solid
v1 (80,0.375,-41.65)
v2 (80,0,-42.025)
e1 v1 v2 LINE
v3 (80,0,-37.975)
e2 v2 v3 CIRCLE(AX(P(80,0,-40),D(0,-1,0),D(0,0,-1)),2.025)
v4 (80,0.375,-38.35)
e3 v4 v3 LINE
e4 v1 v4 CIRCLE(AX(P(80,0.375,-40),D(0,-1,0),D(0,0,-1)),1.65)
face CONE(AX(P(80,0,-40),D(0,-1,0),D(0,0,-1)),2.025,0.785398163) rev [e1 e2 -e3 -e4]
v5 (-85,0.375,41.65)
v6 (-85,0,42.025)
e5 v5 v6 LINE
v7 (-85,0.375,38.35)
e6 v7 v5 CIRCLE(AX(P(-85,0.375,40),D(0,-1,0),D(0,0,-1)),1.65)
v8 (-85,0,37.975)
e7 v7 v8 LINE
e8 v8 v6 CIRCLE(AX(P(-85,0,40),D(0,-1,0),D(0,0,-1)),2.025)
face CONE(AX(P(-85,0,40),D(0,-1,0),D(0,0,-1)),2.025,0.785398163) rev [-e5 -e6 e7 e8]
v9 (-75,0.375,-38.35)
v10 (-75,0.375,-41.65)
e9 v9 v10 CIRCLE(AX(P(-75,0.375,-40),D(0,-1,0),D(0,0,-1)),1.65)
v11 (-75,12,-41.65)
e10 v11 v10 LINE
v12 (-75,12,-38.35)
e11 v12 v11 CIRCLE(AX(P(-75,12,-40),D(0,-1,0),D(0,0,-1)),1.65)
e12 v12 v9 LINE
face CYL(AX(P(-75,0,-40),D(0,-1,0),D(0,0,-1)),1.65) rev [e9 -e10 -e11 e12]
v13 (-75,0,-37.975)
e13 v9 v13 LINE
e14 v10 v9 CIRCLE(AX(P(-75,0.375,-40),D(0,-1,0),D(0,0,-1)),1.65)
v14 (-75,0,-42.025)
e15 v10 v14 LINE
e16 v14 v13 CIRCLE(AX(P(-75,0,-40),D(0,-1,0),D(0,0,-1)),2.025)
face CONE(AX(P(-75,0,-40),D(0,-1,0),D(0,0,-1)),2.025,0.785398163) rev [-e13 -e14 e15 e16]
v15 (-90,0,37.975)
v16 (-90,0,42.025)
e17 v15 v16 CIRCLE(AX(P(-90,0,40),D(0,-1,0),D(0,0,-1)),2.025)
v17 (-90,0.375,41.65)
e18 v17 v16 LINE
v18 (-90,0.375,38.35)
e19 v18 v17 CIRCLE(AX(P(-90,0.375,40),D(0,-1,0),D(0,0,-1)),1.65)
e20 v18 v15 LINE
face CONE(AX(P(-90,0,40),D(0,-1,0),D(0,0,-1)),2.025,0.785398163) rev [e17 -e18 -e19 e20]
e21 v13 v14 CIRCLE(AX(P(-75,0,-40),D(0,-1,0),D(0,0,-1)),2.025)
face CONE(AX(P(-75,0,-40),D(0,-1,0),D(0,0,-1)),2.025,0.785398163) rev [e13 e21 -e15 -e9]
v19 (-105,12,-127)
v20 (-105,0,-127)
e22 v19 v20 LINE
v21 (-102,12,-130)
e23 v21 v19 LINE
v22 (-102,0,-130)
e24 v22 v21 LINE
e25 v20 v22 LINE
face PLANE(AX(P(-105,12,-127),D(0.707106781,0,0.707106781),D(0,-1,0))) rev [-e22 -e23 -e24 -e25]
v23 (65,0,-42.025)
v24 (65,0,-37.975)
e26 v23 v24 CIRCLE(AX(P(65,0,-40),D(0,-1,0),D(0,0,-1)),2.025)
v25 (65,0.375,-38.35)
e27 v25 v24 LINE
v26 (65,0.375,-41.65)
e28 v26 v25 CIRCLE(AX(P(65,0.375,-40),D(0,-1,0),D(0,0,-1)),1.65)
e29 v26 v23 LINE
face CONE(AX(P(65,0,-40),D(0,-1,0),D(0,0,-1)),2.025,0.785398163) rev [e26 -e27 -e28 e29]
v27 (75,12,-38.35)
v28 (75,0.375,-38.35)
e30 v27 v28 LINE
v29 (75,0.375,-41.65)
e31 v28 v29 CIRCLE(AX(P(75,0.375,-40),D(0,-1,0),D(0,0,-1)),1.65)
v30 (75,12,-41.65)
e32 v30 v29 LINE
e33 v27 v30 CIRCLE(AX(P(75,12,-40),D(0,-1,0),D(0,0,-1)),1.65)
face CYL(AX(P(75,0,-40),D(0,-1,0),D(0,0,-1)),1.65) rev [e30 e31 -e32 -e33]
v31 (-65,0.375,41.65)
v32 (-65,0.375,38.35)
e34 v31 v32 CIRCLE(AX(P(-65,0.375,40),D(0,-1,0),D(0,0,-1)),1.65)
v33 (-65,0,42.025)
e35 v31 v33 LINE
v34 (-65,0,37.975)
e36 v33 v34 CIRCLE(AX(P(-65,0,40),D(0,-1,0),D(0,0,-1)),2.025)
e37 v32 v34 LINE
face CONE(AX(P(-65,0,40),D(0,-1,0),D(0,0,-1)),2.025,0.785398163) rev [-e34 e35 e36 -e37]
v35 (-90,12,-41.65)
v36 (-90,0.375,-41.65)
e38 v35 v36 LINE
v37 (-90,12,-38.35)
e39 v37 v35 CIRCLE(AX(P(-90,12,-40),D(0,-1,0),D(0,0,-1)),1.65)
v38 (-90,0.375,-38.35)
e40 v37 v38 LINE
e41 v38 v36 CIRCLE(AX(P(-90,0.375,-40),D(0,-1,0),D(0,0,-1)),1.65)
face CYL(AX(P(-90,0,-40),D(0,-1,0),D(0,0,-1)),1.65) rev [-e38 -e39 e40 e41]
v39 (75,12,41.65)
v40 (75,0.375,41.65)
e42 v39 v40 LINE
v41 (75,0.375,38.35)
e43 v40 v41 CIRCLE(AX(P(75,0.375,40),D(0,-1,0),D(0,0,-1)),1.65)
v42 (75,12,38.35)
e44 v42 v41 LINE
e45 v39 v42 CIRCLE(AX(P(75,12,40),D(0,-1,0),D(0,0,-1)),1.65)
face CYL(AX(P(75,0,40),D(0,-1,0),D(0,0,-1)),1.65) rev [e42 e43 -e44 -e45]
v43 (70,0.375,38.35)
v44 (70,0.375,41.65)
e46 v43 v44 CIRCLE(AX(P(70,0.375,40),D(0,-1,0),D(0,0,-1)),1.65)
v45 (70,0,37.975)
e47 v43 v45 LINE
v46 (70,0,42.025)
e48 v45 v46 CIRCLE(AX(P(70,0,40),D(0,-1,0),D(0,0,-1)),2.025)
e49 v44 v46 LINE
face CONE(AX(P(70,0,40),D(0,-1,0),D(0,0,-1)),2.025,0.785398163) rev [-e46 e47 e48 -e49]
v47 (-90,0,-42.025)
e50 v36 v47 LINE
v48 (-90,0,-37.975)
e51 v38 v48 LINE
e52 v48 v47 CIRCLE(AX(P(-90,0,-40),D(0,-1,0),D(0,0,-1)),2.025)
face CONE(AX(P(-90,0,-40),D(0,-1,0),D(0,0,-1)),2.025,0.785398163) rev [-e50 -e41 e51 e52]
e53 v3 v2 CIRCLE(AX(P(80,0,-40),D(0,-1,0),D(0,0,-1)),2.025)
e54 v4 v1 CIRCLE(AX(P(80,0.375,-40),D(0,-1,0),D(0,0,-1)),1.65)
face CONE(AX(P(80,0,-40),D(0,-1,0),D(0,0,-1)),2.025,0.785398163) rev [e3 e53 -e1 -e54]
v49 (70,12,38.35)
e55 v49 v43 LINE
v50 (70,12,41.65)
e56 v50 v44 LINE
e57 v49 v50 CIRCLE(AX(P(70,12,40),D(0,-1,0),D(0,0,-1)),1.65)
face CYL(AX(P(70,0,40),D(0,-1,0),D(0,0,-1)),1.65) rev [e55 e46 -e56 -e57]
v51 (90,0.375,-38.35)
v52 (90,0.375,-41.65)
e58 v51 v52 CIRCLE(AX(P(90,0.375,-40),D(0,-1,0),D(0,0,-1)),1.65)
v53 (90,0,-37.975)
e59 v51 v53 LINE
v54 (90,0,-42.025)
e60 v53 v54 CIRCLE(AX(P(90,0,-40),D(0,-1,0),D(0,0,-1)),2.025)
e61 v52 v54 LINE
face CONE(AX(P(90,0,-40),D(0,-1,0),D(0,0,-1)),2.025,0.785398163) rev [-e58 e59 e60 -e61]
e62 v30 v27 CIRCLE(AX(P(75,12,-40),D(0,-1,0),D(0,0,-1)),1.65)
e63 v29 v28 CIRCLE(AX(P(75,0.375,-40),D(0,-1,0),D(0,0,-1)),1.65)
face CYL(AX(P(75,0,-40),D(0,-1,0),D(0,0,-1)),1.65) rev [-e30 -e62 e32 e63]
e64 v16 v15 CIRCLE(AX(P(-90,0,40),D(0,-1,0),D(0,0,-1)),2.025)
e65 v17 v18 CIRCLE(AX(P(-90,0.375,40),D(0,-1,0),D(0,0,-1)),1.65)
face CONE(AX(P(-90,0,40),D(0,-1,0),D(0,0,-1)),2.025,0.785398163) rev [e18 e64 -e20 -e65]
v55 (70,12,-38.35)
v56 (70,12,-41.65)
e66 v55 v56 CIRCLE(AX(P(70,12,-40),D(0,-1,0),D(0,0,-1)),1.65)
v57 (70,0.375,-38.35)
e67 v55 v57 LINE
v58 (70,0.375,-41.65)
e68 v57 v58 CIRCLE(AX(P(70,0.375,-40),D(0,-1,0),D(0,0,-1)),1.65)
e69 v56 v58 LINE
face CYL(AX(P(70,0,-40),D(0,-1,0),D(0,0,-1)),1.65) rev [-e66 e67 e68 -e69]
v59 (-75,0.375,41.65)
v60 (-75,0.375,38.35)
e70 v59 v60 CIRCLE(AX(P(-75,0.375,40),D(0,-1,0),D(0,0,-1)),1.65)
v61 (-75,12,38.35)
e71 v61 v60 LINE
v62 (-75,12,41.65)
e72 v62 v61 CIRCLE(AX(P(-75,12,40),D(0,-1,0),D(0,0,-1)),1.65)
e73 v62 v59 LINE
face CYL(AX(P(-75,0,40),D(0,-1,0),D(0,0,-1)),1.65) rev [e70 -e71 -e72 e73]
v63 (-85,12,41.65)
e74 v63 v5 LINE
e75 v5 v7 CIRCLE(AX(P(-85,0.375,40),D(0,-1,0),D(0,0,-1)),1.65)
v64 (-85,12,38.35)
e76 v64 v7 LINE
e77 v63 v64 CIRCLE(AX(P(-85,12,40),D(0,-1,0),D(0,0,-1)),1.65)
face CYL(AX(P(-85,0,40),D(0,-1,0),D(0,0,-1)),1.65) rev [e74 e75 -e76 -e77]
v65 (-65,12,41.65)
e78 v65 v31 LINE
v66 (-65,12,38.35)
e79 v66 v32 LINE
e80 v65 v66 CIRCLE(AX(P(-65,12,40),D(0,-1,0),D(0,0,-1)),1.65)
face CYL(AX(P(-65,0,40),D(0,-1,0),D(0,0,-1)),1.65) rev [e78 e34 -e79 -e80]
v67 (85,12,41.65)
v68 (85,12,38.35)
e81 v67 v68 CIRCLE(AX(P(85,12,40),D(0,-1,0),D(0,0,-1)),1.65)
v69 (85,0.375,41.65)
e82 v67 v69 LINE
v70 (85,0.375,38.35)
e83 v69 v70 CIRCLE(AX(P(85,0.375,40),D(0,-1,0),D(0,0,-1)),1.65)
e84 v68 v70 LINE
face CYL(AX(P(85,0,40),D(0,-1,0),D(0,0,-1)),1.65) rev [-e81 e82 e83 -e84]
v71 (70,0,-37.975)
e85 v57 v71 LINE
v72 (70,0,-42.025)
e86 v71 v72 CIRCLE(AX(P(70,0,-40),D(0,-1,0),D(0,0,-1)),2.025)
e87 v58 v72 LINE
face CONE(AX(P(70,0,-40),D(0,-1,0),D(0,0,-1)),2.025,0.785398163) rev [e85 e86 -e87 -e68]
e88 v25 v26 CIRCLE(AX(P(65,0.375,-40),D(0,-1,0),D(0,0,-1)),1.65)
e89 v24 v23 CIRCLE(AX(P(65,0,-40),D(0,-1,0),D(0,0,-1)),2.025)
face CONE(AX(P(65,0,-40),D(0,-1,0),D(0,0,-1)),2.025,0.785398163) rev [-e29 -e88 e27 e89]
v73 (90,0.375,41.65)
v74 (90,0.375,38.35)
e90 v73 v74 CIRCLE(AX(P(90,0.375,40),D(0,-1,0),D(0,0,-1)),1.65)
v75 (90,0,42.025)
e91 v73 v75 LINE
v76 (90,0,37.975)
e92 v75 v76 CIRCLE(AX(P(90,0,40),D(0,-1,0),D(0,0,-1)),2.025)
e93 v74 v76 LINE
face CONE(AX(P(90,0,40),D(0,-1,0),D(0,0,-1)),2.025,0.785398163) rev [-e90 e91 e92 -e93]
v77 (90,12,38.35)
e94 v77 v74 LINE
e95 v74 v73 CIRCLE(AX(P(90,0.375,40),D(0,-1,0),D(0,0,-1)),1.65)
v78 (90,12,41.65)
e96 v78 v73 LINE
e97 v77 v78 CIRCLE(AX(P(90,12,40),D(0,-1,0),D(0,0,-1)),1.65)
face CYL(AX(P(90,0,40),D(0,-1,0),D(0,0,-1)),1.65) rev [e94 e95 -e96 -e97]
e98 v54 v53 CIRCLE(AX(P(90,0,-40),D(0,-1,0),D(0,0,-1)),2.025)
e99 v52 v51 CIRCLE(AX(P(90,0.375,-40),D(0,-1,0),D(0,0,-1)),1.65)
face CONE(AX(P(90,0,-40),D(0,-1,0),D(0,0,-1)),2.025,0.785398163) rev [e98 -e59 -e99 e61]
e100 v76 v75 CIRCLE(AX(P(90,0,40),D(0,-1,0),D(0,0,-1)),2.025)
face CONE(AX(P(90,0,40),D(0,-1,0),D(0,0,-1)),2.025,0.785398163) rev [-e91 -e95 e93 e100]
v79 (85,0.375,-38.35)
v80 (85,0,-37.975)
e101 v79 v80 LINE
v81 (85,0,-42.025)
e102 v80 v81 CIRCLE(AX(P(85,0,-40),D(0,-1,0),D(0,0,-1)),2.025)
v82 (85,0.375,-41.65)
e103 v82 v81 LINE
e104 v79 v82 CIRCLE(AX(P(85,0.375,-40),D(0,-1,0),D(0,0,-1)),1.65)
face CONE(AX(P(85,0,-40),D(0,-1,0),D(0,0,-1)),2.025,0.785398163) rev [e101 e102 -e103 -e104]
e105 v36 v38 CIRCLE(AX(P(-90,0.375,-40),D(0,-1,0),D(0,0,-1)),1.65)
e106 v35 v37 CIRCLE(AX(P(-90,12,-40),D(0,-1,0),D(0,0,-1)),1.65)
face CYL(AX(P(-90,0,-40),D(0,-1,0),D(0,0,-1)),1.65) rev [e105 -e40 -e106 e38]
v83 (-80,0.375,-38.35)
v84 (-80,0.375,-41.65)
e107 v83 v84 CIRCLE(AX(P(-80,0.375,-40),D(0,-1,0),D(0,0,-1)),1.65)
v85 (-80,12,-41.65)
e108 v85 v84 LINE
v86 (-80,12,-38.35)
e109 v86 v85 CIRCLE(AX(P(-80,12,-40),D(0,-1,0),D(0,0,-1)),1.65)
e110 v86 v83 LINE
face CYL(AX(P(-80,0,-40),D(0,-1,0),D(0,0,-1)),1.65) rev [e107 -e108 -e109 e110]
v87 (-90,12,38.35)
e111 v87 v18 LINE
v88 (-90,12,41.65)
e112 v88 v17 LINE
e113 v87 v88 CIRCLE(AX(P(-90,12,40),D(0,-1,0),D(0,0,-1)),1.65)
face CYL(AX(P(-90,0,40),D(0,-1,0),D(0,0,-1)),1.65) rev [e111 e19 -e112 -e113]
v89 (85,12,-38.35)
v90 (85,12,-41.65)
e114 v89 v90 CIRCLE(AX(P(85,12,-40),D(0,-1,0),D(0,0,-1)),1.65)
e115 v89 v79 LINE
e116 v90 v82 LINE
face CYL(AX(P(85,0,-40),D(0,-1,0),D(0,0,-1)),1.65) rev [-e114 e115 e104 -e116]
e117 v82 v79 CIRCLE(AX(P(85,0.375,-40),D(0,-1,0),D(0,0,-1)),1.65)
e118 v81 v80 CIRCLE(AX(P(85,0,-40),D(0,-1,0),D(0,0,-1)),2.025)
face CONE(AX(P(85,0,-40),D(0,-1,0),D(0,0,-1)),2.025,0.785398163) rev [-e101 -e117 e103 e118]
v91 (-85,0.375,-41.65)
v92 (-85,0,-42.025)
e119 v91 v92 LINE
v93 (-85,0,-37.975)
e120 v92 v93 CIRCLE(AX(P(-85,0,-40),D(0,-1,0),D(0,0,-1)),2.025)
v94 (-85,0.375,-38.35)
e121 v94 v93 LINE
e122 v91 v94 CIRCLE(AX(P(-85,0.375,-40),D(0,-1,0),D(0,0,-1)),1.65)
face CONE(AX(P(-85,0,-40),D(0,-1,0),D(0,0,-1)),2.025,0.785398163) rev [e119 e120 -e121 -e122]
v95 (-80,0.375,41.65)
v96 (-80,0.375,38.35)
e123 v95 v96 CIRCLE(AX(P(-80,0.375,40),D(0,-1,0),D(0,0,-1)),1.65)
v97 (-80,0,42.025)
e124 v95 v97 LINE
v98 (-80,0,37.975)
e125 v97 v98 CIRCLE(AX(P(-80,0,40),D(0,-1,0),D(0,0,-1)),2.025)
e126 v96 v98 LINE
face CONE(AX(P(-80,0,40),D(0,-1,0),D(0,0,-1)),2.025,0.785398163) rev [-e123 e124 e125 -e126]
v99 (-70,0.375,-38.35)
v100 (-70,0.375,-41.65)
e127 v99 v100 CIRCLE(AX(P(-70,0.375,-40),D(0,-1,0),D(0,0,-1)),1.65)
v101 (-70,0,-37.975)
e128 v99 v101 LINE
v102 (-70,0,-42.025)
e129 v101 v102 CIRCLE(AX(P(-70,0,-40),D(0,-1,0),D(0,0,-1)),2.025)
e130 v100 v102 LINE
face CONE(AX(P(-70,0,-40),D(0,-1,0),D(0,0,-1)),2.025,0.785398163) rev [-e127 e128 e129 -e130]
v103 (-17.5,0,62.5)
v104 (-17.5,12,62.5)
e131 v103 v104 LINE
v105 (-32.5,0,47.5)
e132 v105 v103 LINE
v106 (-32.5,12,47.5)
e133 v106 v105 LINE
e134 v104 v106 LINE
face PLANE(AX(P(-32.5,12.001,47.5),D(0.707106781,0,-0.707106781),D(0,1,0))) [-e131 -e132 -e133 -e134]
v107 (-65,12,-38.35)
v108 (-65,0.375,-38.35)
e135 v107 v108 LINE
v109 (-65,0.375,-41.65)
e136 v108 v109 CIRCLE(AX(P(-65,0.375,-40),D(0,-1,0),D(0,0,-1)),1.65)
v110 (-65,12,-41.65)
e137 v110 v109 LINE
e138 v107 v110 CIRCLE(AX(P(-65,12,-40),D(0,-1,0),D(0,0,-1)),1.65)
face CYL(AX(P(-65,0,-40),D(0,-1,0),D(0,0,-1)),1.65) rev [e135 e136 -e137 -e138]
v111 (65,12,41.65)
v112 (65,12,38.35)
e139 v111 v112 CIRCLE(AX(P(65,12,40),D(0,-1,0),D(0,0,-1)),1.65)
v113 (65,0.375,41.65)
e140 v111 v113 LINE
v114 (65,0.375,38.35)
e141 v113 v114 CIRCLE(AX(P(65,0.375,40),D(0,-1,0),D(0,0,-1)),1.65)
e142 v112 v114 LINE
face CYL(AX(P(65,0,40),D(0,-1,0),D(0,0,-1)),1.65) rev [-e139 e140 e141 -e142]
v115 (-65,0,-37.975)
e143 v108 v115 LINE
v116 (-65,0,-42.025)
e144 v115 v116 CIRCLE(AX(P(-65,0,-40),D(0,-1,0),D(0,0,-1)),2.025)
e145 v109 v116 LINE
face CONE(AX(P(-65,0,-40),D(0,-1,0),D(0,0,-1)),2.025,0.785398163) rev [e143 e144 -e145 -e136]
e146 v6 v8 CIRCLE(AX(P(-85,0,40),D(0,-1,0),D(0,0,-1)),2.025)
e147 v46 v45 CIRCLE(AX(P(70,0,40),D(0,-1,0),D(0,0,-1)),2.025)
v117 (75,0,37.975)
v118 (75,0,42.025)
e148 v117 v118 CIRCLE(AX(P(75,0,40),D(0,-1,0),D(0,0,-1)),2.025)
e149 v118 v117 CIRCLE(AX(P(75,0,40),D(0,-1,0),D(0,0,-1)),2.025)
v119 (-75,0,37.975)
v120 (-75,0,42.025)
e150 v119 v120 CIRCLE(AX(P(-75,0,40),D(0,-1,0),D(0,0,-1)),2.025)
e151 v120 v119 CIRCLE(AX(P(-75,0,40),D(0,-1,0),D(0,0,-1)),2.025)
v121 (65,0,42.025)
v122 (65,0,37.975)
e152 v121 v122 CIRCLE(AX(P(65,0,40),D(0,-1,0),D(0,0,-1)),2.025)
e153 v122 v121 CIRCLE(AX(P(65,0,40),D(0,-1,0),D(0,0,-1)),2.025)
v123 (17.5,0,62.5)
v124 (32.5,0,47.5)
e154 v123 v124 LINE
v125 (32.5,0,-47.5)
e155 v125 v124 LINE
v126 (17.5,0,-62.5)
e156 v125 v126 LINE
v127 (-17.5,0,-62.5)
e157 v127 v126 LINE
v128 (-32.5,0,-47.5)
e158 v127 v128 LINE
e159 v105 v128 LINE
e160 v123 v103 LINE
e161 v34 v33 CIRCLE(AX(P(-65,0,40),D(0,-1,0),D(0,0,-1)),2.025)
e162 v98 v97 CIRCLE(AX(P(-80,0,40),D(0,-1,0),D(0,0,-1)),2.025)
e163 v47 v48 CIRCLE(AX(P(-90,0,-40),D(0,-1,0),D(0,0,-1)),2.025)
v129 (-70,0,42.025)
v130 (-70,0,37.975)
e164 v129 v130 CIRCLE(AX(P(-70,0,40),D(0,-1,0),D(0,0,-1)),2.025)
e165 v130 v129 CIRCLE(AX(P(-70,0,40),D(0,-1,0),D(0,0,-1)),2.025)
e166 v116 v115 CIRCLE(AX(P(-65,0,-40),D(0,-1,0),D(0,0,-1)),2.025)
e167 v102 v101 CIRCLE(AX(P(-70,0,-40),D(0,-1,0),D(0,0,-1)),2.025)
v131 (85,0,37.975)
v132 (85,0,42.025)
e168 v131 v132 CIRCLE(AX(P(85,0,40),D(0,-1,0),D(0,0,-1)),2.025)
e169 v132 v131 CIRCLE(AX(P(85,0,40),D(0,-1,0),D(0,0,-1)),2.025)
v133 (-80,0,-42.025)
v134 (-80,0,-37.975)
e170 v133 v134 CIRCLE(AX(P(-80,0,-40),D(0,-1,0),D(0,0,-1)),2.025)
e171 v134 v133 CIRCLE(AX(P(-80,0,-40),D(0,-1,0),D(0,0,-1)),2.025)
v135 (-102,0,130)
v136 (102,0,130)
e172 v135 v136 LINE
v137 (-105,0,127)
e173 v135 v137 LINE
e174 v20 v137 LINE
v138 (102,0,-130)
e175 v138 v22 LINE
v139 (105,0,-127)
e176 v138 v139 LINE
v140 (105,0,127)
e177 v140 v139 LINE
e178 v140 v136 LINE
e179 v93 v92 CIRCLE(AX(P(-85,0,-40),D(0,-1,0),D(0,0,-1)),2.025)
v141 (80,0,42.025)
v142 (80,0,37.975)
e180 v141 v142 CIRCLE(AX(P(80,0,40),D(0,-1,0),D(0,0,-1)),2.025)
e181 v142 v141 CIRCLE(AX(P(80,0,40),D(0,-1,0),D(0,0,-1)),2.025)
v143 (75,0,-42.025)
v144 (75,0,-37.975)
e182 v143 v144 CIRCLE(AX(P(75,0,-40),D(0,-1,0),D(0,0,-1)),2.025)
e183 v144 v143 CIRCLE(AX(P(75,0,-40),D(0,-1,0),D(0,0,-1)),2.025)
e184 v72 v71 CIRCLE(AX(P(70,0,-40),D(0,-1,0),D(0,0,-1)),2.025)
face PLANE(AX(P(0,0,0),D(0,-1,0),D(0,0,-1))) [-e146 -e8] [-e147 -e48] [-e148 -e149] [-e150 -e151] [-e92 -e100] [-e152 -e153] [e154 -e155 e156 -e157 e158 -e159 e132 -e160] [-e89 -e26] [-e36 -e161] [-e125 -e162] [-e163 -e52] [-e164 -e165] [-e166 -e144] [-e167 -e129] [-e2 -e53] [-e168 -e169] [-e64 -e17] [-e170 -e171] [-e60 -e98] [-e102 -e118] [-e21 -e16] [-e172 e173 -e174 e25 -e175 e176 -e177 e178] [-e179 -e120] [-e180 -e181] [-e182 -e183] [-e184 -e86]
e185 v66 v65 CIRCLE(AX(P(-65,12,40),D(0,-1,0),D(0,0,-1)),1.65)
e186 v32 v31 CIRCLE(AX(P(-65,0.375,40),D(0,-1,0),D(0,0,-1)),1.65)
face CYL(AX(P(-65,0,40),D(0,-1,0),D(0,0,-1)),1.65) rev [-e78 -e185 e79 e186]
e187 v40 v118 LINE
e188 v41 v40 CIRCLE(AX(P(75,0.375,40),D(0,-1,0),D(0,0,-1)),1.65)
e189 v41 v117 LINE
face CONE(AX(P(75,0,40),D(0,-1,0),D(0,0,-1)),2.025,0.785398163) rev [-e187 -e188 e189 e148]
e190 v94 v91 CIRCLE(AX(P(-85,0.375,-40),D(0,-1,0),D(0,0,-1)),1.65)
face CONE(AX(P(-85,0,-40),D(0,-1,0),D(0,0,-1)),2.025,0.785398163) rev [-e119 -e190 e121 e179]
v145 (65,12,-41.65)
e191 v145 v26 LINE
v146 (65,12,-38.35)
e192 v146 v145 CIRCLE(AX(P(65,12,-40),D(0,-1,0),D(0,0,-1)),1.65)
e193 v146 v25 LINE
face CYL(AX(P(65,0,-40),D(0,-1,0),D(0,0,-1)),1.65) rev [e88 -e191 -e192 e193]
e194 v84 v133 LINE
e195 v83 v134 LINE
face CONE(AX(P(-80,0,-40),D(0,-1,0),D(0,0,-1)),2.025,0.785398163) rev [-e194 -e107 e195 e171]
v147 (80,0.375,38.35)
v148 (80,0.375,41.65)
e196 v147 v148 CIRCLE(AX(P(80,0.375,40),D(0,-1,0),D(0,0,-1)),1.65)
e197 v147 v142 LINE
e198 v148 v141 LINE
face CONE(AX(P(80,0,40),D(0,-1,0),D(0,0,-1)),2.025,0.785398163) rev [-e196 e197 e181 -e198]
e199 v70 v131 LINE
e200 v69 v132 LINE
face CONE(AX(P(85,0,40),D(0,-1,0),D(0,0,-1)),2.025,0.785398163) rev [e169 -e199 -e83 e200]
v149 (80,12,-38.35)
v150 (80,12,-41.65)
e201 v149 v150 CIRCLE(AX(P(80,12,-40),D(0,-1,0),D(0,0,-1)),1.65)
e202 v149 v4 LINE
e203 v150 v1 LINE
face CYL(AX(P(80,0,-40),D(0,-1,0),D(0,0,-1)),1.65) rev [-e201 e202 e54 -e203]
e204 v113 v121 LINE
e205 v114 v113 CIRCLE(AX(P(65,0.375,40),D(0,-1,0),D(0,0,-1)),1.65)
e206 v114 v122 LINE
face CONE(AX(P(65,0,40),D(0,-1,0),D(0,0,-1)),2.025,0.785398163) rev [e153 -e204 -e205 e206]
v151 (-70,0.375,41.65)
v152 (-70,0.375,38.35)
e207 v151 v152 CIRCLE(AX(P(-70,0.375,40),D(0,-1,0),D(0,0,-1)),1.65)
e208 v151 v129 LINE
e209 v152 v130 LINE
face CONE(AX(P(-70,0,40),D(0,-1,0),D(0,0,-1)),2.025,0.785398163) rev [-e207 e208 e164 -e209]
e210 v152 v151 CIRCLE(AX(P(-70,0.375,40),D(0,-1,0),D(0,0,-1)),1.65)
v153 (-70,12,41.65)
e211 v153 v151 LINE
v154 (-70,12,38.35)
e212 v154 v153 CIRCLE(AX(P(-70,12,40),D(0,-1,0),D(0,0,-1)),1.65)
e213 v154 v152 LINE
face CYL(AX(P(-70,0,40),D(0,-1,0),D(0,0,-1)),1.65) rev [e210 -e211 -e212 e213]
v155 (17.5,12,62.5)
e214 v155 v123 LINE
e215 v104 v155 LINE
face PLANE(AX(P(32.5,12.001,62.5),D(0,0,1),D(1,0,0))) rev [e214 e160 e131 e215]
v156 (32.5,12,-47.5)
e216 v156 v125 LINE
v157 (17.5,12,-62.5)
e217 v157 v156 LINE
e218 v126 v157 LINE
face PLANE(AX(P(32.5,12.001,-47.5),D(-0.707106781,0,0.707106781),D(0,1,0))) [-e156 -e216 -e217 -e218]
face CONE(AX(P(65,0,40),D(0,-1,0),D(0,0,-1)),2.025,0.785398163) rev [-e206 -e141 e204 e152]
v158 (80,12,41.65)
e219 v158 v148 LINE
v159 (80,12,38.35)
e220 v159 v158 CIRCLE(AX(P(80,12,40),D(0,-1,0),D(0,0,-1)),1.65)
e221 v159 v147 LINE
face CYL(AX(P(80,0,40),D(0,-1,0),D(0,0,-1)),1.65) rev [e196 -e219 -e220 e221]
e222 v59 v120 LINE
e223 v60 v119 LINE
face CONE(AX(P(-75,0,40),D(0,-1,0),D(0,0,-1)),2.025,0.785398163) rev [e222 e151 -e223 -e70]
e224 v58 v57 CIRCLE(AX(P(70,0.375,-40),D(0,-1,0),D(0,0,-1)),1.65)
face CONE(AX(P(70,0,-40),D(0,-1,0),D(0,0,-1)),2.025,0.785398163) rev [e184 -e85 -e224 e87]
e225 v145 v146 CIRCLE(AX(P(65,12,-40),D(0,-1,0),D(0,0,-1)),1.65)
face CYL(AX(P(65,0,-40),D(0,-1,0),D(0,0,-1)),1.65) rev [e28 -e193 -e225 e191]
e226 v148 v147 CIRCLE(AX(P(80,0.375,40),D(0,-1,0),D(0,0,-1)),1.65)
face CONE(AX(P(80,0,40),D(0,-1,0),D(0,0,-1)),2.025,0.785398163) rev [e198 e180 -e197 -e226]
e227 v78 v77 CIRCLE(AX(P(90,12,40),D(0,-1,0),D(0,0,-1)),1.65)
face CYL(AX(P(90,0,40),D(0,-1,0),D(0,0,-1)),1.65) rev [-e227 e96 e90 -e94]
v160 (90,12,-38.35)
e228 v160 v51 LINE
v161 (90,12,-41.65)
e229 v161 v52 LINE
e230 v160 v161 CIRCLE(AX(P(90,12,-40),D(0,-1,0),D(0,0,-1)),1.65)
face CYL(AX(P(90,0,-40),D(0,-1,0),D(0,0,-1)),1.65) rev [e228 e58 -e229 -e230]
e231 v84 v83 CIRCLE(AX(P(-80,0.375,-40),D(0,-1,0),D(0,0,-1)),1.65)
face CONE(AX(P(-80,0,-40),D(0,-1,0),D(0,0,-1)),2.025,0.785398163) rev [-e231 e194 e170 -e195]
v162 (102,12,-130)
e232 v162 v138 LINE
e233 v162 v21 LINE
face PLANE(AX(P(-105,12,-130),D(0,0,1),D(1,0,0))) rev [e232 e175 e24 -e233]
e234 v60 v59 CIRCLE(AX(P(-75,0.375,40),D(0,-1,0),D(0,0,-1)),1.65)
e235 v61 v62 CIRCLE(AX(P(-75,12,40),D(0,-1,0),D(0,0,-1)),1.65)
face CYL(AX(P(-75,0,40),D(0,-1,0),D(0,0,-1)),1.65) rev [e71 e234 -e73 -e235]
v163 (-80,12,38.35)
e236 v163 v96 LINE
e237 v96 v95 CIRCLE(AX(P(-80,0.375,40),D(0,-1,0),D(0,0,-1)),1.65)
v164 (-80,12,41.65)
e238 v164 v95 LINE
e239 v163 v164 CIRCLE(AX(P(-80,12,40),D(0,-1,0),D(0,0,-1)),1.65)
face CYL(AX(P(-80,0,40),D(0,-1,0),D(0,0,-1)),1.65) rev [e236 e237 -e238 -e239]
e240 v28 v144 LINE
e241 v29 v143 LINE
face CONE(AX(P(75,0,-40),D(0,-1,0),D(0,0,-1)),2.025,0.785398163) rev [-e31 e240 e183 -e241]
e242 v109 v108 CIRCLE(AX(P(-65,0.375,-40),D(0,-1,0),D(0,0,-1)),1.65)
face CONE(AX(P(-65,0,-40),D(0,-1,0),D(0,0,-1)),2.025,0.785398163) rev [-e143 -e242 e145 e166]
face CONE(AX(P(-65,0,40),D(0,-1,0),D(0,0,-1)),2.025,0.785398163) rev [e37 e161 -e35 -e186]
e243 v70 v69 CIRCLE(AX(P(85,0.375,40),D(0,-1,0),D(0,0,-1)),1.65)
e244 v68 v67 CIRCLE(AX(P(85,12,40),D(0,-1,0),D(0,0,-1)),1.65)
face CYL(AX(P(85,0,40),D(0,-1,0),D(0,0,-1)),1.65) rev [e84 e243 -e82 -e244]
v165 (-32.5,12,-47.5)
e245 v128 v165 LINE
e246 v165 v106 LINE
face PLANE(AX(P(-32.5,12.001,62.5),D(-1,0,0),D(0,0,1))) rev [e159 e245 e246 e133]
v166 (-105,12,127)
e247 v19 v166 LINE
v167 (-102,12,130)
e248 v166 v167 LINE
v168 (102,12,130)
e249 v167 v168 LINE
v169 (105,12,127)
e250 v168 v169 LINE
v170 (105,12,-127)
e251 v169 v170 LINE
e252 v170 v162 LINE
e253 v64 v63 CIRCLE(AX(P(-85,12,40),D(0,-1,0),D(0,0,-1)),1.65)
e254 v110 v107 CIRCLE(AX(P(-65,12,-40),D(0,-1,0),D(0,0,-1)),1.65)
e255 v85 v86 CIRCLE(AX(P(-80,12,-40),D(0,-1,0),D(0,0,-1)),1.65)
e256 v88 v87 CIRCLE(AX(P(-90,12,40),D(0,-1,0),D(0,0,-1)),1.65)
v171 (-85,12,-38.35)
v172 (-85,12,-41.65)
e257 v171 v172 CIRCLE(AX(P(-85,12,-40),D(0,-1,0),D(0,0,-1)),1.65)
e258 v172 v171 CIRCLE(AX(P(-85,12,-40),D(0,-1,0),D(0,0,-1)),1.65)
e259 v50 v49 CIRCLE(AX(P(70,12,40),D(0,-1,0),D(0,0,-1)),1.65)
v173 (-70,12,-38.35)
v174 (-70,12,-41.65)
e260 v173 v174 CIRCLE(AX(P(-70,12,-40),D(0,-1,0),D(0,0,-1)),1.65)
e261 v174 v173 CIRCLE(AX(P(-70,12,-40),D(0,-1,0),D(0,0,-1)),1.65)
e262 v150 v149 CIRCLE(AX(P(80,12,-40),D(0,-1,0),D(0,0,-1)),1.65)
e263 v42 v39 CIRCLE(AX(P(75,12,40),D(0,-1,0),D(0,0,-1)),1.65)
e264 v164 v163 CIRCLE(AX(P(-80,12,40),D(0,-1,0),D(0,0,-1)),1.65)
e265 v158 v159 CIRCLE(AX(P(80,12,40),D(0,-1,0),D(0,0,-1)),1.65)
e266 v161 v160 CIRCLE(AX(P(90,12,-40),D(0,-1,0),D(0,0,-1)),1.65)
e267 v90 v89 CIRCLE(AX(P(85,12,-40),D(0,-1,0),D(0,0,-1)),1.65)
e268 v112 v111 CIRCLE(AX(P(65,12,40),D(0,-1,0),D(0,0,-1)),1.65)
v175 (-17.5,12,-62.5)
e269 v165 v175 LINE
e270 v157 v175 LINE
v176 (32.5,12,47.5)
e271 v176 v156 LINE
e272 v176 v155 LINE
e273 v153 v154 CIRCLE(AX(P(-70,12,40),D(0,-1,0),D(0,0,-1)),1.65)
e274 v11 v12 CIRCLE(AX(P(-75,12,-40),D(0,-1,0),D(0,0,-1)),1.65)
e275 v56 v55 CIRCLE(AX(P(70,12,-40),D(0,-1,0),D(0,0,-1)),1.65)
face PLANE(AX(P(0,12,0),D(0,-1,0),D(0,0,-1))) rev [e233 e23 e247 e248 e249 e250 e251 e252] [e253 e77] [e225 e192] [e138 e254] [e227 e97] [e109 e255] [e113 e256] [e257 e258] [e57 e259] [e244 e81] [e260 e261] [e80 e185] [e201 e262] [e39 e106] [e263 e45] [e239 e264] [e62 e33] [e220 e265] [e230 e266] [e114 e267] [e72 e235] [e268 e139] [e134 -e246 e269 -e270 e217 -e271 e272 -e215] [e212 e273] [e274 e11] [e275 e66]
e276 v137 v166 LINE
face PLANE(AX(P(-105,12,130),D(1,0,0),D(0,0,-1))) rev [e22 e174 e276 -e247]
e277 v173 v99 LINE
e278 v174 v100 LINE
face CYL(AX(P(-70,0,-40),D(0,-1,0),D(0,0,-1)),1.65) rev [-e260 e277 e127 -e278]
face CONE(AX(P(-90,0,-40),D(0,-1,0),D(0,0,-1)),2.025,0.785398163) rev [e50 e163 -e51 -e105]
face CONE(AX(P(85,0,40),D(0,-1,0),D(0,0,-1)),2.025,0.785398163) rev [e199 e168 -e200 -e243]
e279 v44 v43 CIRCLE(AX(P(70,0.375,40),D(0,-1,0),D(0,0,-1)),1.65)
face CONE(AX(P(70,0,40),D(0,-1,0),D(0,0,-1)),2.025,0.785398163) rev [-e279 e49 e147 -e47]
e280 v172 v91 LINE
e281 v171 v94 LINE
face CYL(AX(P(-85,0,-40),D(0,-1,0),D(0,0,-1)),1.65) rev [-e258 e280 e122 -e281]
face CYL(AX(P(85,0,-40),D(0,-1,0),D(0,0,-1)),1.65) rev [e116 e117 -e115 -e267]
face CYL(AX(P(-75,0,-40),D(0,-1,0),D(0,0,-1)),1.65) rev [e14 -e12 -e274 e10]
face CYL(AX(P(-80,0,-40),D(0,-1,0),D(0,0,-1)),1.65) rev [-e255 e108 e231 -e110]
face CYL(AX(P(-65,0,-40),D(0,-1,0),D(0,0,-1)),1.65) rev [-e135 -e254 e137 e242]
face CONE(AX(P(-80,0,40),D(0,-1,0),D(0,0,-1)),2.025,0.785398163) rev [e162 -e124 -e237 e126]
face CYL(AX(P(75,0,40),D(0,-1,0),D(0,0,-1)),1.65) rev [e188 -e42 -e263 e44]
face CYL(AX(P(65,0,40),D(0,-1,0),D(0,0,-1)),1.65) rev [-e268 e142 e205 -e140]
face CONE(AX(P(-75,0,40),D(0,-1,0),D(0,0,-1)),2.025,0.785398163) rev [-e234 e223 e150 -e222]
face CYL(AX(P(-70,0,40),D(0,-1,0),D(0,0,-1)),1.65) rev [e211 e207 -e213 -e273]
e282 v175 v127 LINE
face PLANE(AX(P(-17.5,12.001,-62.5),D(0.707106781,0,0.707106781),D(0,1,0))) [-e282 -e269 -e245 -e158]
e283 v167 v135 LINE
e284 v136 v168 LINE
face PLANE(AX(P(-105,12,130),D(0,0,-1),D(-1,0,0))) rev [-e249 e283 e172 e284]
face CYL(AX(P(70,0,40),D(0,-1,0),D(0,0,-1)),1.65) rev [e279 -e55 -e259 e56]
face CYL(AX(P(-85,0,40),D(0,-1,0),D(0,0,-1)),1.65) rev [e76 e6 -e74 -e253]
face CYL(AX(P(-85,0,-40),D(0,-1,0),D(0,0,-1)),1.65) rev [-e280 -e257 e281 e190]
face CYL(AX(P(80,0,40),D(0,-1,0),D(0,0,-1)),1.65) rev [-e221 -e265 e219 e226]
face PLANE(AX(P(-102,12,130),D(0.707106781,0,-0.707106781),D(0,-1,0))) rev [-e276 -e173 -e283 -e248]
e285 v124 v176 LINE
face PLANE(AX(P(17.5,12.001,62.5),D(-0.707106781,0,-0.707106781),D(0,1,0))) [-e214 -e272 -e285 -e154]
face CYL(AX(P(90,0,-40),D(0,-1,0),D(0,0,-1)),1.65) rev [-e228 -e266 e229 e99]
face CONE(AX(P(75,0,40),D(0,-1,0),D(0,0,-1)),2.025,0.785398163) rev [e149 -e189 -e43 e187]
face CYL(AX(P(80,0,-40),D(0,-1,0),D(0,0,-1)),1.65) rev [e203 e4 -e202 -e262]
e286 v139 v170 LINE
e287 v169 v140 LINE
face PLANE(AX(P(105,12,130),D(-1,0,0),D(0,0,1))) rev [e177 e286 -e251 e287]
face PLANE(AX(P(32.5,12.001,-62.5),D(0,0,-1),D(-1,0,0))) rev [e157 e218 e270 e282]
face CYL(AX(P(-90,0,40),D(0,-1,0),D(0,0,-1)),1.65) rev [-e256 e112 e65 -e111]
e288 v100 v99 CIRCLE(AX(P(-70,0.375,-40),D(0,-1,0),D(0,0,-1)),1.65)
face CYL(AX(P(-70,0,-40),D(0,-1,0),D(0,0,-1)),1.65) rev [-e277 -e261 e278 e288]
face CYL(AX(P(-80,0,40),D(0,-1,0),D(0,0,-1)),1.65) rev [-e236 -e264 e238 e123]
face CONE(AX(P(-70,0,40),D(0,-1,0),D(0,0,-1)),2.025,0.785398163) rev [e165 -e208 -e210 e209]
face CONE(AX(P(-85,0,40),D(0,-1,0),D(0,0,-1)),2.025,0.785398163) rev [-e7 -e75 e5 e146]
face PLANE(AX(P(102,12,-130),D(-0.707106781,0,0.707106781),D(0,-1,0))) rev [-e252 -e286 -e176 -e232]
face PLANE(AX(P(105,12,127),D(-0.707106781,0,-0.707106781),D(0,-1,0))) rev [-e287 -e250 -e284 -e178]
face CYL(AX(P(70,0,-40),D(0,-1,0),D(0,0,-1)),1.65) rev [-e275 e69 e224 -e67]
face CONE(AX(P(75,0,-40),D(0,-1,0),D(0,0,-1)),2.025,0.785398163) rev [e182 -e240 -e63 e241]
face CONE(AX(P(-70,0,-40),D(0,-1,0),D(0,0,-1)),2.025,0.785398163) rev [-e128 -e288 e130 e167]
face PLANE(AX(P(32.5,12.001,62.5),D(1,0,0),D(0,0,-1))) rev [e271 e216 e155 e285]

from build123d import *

# Parameters (mm, degrees)
SKETCH_1_W                   = 210
SKETCH_1_H                   = 260
EXTRUDE_1_DEPTH              = 12
HOLE_WIZARD_M4_1_D           = 3.3
HOLE_WIZARD_M4_1_CSINK_D     = 4.05
HOLE_WIZARD_M4_1_CSINK_ANGLE = 90
PATTERN_LINEAR_1_COUNT       = 6
PATTERN_LINEAR_1_PITCH       = 5
MIRROR_1_COPY_1_D            = 3.3
MIRROR_1_COPY_1_CSINK_D      = 4.05
MIRROR_1_COPY_1_CSINK_ANGLE  = 90
MIRROR_1_COPY_2_D            = 3.3
MIRROR_1_COPY_2_CSINK_D      = 4.05
MIRROR_1_COPY_2_CSINK_ANGLE  = 90
MIRROR_1_COPY_3_D            = 3.3
MIRROR_1_COPY_3_CSINK_D      = 4.05
MIRROR_1_COPY_3_CSINK_ANGLE  = 90
MIRROR_1_COPY_4_D            = 3.3
MIRROR_1_COPY_4_CSINK_D      = 4.05
MIRROR_1_COPY_4_CSINK_ANGLE  = 90
MIRROR_1_COPY_5_D            = 3.3
MIRROR_1_COPY_5_CSINK_D      = 4.05
MIRROR_1_COPY_5_CSINK_ANGLE  = 90
MIRROR_2_COPY_1_D            = 3.3
MIRROR_2_COPY_1_CSINK_D      = 4.05
MIRROR_2_COPY_1_CSINK_ANGLE  = 90
MIRROR_2_COPY_2_D            = 3.3
MIRROR_2_COPY_2_CSINK_D      = 4.05
MIRROR_2_COPY_2_CSINK_ANGLE  = 90
MIRROR_2_COPY_3_D            = 3.3
MIRROR_2_COPY_3_CSINK_D      = 4.05
MIRROR_2_COPY_3_CSINK_ANGLE  = 90
MIRROR_2_COPY_4_D            = 3.3
MIRROR_2_COPY_4_CSINK_D      = 4.05
MIRROR_2_COPY_4_CSINK_ANGLE  = 90
MIRROR_2_COPY_5_D            = 3.3
MIRROR_2_COPY_5_CSINK_D      = 4.05
MIRROR_2_COPY_5_CSINK_ANGLE  = 90
MIRROR_2_COPY_6_D            = 3.3
MIRROR_2_COPY_6_CSINK_D      = 4.05
MIRROR_2_COPY_6_CSINK_ANGLE  = 90
MIRROR_2_COPY_7_D            = 3.3
MIRROR_2_COPY_7_CSINK_D      = 4.05
MIRROR_2_COPY_7_CSINK_ANGLE  = 90
MIRROR_2_COPY_8_D            = 3.3
MIRROR_2_COPY_8_CSINK_D      = 4.05
MIRROR_2_COPY_8_CSINK_ANGLE  = 90
MIRROR_2_COPY_9_D            = 3.3
MIRROR_2_COPY_9_CSINK_D      = 4.05
MIRROR_2_COPY_9_CSINK_ANGLE  = 90
MIRROR_2_COPY_10_D           = 3.3
MIRROR_2_COPY_10_CSINK_D     = 4.05
MIRROR_2_COPY_10_CSINK_ANGLE = 90
MIRROR_2_COPY_11_D           = 3.3
MIRROR_2_COPY_11_CSINK_D     = 4.05
MIRROR_2_COPY_11_CSINK_ANGLE = 90
CHAMFER_1_SIZE               = 3
CUT_EXTRUDE_1_REACH          = 169.538
SKETCH_3_W                   = 65
SKETCH_3_H                   = 125
CHAMFER_2_SIZE               = 15


with BuildPart() as part:
    # 草图1 → 凸台-拉伸1 (new body)
    with BuildSketch(Plane(origin=(0, 0, 0), x_dir=(1, 0, 0), z_dir=(0, 1, 0))):
        Rectangle(SKETCH_1_W, SKETCH_1_H)
    extrude(amount=EXTRUDE_1_DEPTH)

    # M4 螺纹孔1 (through all)
    with Locations(Plane(origin=(-90, 0, -40), x_dir=(0, 0, -1), z_dir=(0, -1, 0))):
        with Locations((0, 0)):
            hole_wizard_m4_1 = CounterSinkHole(HOLE_WIZARD_M4_1_D / 2, HOLE_WIZARD_M4_1_CSINK_D / 2, counter_sink_angle=HOLE_WIZARD_M4_1_CSINK_ANGLE)

    # 阵列(线性)1: M4 螺纹孔1 ×6
    with Locations(*[(i * PATTERN_LINEAR_1_PITCH, 0, 0) for i in range(1, PATTERN_LINEAR_1_COUNT)]):
        add(hole_wizard_m4_1, mode=Mode.SUBTRACT)

    # 镜向1: M4 螺纹孔1 across plane
    add(hole_wizard_m4_1.mirror(Plane(origin=(0, 0, 0), x_dir=(0, 0, 1), z_dir=(1, 0, 0))), mode=Mode.SUBTRACT)

    # 镜向1 copy 1 (through all)
    with Locations(Plane(origin=(85, 0, -40), x_dir=(0, 0, -1), z_dir=(0, -1, 0))):
        with Locations((0, 0)):
            CounterSinkHole(MIRROR_1_COPY_1_D / 2, MIRROR_1_COPY_1_CSINK_D / 2, counter_sink_angle=MIRROR_1_COPY_1_CSINK_ANGLE)

    # 镜向1 copy 2 (through all)
    with Locations(Plane(origin=(80, 0, -40), x_dir=(0, 0, -1), z_dir=(0, -1, 0))):
        with Locations((0, 0)):
            CounterSinkHole(MIRROR_1_COPY_2_D / 2, MIRROR_1_COPY_2_CSINK_D / 2, counter_sink_angle=MIRROR_1_COPY_2_CSINK_ANGLE)

    # 镜向1 copy 3 (through all)
    with Locations(Plane(origin=(75, 0, -40), x_dir=(0, 0, -1), z_dir=(0, -1, 0))):
        with Locations((0, 0)):
            CounterSinkHole(MIRROR_1_COPY_3_D / 2, MIRROR_1_COPY_3_CSINK_D / 2, counter_sink_angle=MIRROR_1_COPY_3_CSINK_ANGLE)

    # 镜向1 copy 4 (through all)
    with Locations(Plane(origin=(70, 0, -40), x_dir=(0, 0, -1), z_dir=(0, -1, 0))):
        with Locations((0, 0)):
            CounterSinkHole(MIRROR_1_COPY_4_D / 2, MIRROR_1_COPY_4_CSINK_D / 2, counter_sink_angle=MIRROR_1_COPY_4_CSINK_ANGLE)

    # 镜向1 copy 5 (through all)
    with Locations(Plane(origin=(65, 0, -40), x_dir=(0, 0, -1), z_dir=(0, -1, 0))):
        with Locations((0, 0)):
            CounterSinkHole(MIRROR_1_COPY_5_D / 2, MIRROR_1_COPY_5_CSINK_D / 2, counter_sink_angle=MIRROR_1_COPY_5_CSINK_ANGLE)

    # 镜向2: M4 螺纹孔1 across plane
    add(hole_wizard_m4_1.mirror(Plane.XY), mode=Mode.SUBTRACT)

    # 镜向2 copy 1 (through all)
    with Locations(Plane(origin=(-85, 0, 40), x_dir=(0, 0, 1), z_dir=(0, -1, 0))):
        with Locations((0, 0)):
            CounterSinkHole(MIRROR_2_COPY_1_D / 2, MIRROR_2_COPY_1_CSINK_D / 2, counter_sink_angle=MIRROR_2_COPY_1_CSINK_ANGLE)

    # 镜向2 copy 2 (through all)
    with Locations(Plane(origin=(-80, 0, 40), x_dir=(0, 0, 1), z_dir=(0, -1, 0))):
        with Locations((0, 0)):
            CounterSinkHole(MIRROR_2_COPY_2_D / 2, MIRROR_2_COPY_2_CSINK_D / 2, counter_sink_angle=MIRROR_2_COPY_2_CSINK_ANGLE)

    # 镜向2 copy 3 (through all)
    with Locations(Plane(origin=(-75, 0, 40), x_dir=(0, 0, 1), z_dir=(0, -1, 0))):
        with Locations((0, 0)):
            CounterSinkHole(MIRROR_2_COPY_3_D / 2, MIRROR_2_COPY_3_CSINK_D / 2, counter_sink_angle=MIRROR_2_COPY_3_CSINK_ANGLE)

    # 镜向2 copy 4 (through all)
    with Locations(Plane(origin=(-70, 0, 40), x_dir=(0, 0, 1), z_dir=(0, -1, 0))):
        with Locations((0, 0)):
            CounterSinkHole(MIRROR_2_COPY_4_D / 2, MIRROR_2_COPY_4_CSINK_D / 2, counter_sink_angle=MIRROR_2_COPY_4_CSINK_ANGLE)

    # 镜向2 copy 5 (through all)
    with Locations(Plane(origin=(-65, 0, 40), x_dir=(0, 0, 1), z_dir=(0, -1, 0))):
        with Locations((0, 0)):
            CounterSinkHole(MIRROR_2_COPY_5_D / 2, MIRROR_2_COPY_5_CSINK_D / 2, counter_sink_angle=MIRROR_2_COPY_5_CSINK_ANGLE)

    # 镜向2 copy 6 (through all)
    with Locations(Plane(origin=(90, 0, 40), x_dir=(0, 0, 1), z_dir=(0, -1, 0))):
        with Locations((0, 0)):
            CounterSinkHole(MIRROR_2_COPY_6_D / 2, MIRROR_2_COPY_6_CSINK_D / 2, counter_sink_angle=MIRROR_2_COPY_6_CSINK_ANGLE)

    # 镜向2 copy 7 (through all)
    with Locations(Plane(origin=(85, 0, 40), x_dir=(0, 0, 1), z_dir=(0, -1, 0))):
        with Locations((0, 0)):
            CounterSinkHole(MIRROR_2_COPY_7_D / 2, MIRROR_2_COPY_7_CSINK_D / 2, counter_sink_angle=MIRROR_2_COPY_7_CSINK_ANGLE)

    # 镜向2 copy 8 (through all)
    with Locations(Plane(origin=(80, 0, 40), x_dir=(0, 0, 1), z_dir=(0, -1, 0))):
        with Locations((0, 0)):
            CounterSinkHole(MIRROR_2_COPY_8_D / 2, MIRROR_2_COPY_8_CSINK_D / 2, counter_sink_angle=MIRROR_2_COPY_8_CSINK_ANGLE)

    # 镜向2 copy 9 (through all)
    with Locations(Plane(origin=(75, 0, 40), x_dir=(0, 0, 1), z_dir=(0, -1, 0))):
        with Locations((0, 0)):
            CounterSinkHole(MIRROR_2_COPY_9_D / 2, MIRROR_2_COPY_9_CSINK_D / 2, counter_sink_angle=MIRROR_2_COPY_9_CSINK_ANGLE)

    # 镜向2 copy 10 (through all)
    with Locations(Plane(origin=(70, 0, 40), x_dir=(0, 0, 1), z_dir=(0, -1, 0))):
        with Locations((0, 0)):
            CounterSinkHole(MIRROR_2_COPY_10_D / 2, MIRROR_2_COPY_10_CSINK_D / 2, counter_sink_angle=MIRROR_2_COPY_10_CSINK_ANGLE)

    # 镜向2 copy 11 (through all)
    with Locations(Plane(origin=(65, 0, 40), x_dir=(0, 0, 1), z_dir=(0, -1, 0))):
        with Locations((0, 0)):
            CounterSinkHole(MIRROR_2_COPY_11_D / 2, MIRROR_2_COPY_11_CSINK_D / 2, counter_sink_angle=MIRROR_2_COPY_11_CSINK_ANGLE)

    # 倒角1
    chamfer_1_edges = [part.edges().sort_by_distance(p)[0] for p in [
        (105, 6, 130),
        (-105, 6, 130),
        (-105, 6, -130),
        (105, 6, -130),
    ]]
    chamfer(chamfer_1_edges, length=CHAMFER_1_SIZE)

    # 草图3 → 切除-拉伸1 (cut, up to next)
    with BuildSketch(Plane.XZ, mode=Mode.PRIVATE) as cut_extrude_1_sk1:
        Rectangle(SKETCH_3_W, SKETCH_3_H)
    cut_extrude_1_tool1 = extrude(cut_extrude_1_sk1.sketch, amount=-CUT_EXTRUDE_1_REACH, mode=Mode.PRIVATE) & part.part
    add(cut_extrude_1_tool1.solids().sort_by_distance((0, 0, 0))[0], mode=Mode.SUBTRACT)

    # 倒角2
    chamfer_2_edges = [part.edges().sort_by_distance(p)[0] for p in [
        (-32.5, 6, -62.5),
        (-32.5, 6, 62.5),
        (32.5, 6, 62.5),
        (32.5, 6, -62.5),
    ]]
    chamfer(chamfer_2_edges, length=CHAMFER_2_SIZE)


solid = part.part
